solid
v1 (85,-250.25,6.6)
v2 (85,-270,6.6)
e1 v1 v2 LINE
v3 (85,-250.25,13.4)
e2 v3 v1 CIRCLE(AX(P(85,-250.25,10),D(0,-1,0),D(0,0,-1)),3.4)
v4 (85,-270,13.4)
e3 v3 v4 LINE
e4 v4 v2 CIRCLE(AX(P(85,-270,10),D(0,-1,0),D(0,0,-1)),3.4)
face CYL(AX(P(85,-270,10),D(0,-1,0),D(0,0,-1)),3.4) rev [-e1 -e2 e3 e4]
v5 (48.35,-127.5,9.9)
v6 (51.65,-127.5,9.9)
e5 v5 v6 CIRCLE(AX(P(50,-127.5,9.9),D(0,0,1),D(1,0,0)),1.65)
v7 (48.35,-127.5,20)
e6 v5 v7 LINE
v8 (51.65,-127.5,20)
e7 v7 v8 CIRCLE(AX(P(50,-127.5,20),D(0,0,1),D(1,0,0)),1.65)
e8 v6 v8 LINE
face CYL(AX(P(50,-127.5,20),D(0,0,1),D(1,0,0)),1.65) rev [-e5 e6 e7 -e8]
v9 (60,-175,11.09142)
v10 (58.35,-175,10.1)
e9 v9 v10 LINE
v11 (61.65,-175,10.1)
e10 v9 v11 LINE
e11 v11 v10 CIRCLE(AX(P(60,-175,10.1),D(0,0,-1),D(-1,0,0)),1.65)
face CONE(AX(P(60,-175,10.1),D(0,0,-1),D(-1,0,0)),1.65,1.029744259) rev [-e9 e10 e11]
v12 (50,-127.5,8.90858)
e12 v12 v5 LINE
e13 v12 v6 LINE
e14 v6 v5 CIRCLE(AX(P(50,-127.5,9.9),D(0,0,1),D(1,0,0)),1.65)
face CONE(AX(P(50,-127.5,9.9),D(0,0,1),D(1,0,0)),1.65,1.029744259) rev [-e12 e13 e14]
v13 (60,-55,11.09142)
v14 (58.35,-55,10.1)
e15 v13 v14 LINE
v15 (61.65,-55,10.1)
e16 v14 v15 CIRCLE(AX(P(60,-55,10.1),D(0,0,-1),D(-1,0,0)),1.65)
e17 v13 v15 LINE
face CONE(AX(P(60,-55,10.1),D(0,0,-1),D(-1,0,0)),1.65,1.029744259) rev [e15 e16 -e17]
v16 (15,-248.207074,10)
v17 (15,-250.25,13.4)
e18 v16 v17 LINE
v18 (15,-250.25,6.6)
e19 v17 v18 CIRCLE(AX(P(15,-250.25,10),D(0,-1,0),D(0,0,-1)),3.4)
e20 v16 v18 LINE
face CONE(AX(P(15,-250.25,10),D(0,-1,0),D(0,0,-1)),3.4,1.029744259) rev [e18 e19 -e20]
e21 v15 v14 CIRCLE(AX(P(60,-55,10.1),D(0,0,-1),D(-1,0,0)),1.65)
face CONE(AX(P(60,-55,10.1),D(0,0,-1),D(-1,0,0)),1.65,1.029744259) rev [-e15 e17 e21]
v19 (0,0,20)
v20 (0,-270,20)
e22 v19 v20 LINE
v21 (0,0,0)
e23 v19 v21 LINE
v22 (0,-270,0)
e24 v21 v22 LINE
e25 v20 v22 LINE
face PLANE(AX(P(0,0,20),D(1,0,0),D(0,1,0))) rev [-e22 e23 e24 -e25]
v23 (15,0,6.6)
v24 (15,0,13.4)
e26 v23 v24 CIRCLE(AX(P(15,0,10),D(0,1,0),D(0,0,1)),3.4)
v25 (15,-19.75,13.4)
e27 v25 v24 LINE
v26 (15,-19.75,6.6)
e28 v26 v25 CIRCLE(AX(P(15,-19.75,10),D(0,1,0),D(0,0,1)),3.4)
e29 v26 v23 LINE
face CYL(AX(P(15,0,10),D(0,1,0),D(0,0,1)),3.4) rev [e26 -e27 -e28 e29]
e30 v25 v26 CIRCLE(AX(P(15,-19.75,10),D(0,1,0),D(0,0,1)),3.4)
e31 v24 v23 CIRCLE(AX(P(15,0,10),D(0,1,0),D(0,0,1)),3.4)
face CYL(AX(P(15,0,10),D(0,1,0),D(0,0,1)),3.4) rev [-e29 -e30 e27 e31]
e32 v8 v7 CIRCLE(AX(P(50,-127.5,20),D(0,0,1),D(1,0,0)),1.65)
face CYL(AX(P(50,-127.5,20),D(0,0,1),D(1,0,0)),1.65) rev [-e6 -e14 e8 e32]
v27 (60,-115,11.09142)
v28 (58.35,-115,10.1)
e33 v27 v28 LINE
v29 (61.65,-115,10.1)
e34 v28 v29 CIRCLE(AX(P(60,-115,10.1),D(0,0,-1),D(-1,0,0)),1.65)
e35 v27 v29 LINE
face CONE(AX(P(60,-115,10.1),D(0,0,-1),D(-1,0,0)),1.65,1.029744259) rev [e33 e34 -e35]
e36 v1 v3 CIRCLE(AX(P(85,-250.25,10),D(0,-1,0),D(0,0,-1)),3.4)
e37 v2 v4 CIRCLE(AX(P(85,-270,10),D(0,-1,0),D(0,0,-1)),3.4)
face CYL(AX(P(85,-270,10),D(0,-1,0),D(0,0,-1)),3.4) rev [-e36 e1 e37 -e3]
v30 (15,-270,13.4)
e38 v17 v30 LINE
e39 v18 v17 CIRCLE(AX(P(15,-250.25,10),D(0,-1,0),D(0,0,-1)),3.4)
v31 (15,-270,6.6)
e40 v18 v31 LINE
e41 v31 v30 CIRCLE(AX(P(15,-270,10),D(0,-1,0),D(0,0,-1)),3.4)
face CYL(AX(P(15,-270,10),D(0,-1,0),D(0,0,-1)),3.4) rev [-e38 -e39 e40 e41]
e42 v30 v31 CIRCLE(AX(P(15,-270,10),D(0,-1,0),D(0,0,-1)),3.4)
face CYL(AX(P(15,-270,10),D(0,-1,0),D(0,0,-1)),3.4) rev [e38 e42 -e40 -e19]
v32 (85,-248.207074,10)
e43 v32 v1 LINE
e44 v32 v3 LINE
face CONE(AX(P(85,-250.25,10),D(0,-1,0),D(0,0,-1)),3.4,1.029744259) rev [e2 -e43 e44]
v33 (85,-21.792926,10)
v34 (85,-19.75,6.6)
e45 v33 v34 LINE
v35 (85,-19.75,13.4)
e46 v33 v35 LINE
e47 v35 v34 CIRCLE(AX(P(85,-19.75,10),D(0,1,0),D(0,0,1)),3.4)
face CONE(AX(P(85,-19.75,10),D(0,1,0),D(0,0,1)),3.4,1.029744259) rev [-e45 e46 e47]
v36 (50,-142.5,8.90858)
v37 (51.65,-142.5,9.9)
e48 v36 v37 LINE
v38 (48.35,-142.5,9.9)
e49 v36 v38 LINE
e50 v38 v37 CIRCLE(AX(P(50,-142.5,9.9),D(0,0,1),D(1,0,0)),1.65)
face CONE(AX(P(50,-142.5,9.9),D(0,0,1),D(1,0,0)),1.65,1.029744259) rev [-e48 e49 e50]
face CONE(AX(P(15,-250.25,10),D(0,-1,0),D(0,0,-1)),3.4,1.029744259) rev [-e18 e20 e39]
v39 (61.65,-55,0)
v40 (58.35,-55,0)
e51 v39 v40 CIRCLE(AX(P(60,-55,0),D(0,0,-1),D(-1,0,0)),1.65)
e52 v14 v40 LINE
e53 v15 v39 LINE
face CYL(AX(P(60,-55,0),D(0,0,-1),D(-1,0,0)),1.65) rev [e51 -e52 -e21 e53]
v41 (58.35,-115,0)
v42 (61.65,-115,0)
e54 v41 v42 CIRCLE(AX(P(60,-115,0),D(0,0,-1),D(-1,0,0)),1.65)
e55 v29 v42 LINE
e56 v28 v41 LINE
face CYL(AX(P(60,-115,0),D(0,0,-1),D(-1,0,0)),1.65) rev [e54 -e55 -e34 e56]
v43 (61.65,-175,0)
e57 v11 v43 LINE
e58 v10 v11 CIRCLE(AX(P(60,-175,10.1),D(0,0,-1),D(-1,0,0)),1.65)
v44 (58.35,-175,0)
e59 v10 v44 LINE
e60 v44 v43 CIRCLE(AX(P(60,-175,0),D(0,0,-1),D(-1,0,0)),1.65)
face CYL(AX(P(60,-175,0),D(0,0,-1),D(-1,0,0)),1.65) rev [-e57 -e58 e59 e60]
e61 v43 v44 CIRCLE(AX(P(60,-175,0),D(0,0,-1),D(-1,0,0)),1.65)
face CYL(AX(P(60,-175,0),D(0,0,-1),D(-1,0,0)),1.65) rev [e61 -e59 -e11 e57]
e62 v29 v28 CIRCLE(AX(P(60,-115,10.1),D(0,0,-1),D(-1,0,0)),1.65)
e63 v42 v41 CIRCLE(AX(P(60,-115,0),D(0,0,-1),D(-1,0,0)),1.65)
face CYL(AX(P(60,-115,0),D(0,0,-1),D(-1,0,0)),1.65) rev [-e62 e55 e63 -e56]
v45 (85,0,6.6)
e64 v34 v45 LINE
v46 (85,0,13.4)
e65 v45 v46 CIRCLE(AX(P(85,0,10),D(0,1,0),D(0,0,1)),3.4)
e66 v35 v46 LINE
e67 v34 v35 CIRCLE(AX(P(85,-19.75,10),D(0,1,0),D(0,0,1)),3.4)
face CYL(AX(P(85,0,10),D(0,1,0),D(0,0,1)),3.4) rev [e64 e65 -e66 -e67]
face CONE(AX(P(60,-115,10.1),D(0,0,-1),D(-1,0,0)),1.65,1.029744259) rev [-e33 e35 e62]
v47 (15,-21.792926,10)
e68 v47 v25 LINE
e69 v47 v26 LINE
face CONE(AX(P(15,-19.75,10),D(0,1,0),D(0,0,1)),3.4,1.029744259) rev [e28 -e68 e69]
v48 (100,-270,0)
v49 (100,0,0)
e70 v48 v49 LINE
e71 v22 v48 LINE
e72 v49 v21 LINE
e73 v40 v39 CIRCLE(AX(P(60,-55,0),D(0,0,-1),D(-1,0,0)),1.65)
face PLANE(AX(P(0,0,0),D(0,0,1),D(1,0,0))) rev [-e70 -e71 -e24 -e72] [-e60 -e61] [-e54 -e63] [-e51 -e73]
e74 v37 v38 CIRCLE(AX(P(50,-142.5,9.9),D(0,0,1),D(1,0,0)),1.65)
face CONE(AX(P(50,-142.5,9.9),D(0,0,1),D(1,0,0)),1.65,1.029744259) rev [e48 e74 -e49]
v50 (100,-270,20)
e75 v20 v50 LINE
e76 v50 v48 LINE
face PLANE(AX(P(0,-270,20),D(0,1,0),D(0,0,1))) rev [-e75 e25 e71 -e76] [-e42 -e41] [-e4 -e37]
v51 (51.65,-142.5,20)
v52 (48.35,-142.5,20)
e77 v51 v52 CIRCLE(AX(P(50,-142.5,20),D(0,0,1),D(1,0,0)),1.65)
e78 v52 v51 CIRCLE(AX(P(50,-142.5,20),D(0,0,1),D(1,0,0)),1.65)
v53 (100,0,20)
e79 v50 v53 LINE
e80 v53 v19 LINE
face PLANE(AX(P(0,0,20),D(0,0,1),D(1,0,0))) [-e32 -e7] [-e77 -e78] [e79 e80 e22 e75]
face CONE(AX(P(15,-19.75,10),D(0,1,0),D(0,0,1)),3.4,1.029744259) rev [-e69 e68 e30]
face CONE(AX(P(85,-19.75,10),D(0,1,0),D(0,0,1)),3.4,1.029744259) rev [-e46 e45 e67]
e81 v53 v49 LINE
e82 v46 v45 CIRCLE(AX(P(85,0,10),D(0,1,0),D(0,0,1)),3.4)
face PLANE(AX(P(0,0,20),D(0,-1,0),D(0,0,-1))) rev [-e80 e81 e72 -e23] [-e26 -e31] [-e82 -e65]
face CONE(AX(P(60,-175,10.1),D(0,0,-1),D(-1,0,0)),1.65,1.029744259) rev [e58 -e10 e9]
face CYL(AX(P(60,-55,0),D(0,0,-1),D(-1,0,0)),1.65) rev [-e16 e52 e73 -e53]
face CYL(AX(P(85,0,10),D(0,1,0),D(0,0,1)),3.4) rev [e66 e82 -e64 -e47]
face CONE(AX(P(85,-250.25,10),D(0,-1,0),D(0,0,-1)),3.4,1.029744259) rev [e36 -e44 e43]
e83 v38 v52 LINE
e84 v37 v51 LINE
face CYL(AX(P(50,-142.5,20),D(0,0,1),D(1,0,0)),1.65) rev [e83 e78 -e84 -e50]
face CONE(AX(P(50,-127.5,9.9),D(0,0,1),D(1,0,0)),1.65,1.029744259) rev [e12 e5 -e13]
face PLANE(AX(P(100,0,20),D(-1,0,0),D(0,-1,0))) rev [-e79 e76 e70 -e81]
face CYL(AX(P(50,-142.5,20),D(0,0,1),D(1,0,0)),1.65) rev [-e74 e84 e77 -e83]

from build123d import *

# Parameters (mm, degrees)
SKETCH1_W                       = 100
SKETCH1_H                       = 270
BOSS_EXTRUDE1_DEPTH             = 20
M8_TAPPED_HOLE1_D               = 6.8
M8_TAPPED_HOLE1_DEPTH           = 19.75
M8_TAPPED_HOLE1_TIP             = 2.042926105
M8_TAPPED_HOLE1_ON_FACE_2_D     = 6.8
M8_TAPPED_HOLE1_ON_FACE_2_DEPTH = 19.75
M8_TAPPED_HOLE1_ON_FACE_2_TIP   = 2.042926105
M4_TAPPED_HOLE2_D               = 3.3
M4_TAPPED_HOLE2_DEPTH           = 10.1
M4_TAPPED_HOLE2_TIP             = 0.991420021
M4_TAPPED_HOLE1_D               = 3.3
M4_TAPPED_HOLE1_DEPTH           = 10.1
M4_TAPPED_HOLE1_TIP             = 0.991420021


with BuildPart() as part:
    # Sketch1 → Boss-Extrude1 (new body)
    with BuildSketch(Plane.XY):
        with Locations((50, -135)):
            Rectangle(SKETCH1_W, SKETCH1_H)
    extrude(amount=BOSS_EXTRUDE1_DEPTH)

    # M8 Tapped Hole1
    with Locations(Plane(origin=(15, 0, 10), x_dir=(0, 0, 1), z_dir=(0, 1, 0))):
        with Locations((0, 0), (0, 70)):
            Hole(M8_TAPPED_HOLE1_D / 2, depth=M8_TAPPED_HOLE1_DEPTH)
            with Locations((0, 0, -(M8_TAPPED_HOLE1_DEPTH + M8_TAPPED_HOLE1_TIP / 2))):  # 118° drill point
                Cone(0, M8_TAPPED_HOLE1_D / 2, M8_TAPPED_HOLE1_TIP, mode=Mode.SUBTRACT)

    # M8 Tapped Hole1 on face 2
    with Locations(Plane(origin=(15, -270, 10), x_dir=(0, 0, -1), z_dir=(0, -1, 0))):
        with Locations((0, 0), (0, 70)):
            Hole(M8_TAPPED_HOLE1_ON_FACE_2_D / 2, depth=M8_TAPPED_HOLE1_ON_FACE_2_DEPTH)
            with Locations((0, 0, -(M8_TAPPED_HOLE1_ON_FACE_2_DEPTH + M8_TAPPED_HOLE1_ON_FACE_2_TIP / 2))):  # 118° drill point
                Cone(0, M8_TAPPED_HOLE1_ON_FACE_2_D / 2, M8_TAPPED_HOLE1_ON_FACE_2_TIP, mode=Mode.SUBTRACT)

    # M4 Tapped Hole2
    with Locations(Plane.XY.offset(20)):
        with Locations((50, -127.5), (50, -142.5)):
            Hole(M4_TAPPED_HOLE2_D / 2, depth=M4_TAPPED_HOLE2_DEPTH)
            with Locations((0, 0, -(M4_TAPPED_HOLE2_DEPTH + M4_TAPPED_HOLE2_TIP / 2))):  # 118° drill point
                Cone(0, M4_TAPPED_HOLE2_D / 2, M4_TAPPED_HOLE2_TIP, mode=Mode.SUBTRACT)

    # M4 Tapped Hole1
    with Locations(Plane(origin=(0, 0, 0), x_dir=(-1, 0, 0), z_dir=(0, 0, -1))):
        with Locations((-60, -55), (-60, -115), (-60, -175)):
            Hole(M4_TAPPED_HOLE1_D / 2, depth=M4_TAPPED_HOLE1_DEPTH)
            with Locations((0, 0, -(M4_TAPPED_HOLE1_DEPTH + M4_TAPPED_HOLE1_TIP / 2))):  # 118° drill point
                Cone(0, M4_TAPPED_HOLE1_D / 2, M4_TAPPED_HOLE1_TIP, mode=Mode.SUBTRACT)


solid = part.part
